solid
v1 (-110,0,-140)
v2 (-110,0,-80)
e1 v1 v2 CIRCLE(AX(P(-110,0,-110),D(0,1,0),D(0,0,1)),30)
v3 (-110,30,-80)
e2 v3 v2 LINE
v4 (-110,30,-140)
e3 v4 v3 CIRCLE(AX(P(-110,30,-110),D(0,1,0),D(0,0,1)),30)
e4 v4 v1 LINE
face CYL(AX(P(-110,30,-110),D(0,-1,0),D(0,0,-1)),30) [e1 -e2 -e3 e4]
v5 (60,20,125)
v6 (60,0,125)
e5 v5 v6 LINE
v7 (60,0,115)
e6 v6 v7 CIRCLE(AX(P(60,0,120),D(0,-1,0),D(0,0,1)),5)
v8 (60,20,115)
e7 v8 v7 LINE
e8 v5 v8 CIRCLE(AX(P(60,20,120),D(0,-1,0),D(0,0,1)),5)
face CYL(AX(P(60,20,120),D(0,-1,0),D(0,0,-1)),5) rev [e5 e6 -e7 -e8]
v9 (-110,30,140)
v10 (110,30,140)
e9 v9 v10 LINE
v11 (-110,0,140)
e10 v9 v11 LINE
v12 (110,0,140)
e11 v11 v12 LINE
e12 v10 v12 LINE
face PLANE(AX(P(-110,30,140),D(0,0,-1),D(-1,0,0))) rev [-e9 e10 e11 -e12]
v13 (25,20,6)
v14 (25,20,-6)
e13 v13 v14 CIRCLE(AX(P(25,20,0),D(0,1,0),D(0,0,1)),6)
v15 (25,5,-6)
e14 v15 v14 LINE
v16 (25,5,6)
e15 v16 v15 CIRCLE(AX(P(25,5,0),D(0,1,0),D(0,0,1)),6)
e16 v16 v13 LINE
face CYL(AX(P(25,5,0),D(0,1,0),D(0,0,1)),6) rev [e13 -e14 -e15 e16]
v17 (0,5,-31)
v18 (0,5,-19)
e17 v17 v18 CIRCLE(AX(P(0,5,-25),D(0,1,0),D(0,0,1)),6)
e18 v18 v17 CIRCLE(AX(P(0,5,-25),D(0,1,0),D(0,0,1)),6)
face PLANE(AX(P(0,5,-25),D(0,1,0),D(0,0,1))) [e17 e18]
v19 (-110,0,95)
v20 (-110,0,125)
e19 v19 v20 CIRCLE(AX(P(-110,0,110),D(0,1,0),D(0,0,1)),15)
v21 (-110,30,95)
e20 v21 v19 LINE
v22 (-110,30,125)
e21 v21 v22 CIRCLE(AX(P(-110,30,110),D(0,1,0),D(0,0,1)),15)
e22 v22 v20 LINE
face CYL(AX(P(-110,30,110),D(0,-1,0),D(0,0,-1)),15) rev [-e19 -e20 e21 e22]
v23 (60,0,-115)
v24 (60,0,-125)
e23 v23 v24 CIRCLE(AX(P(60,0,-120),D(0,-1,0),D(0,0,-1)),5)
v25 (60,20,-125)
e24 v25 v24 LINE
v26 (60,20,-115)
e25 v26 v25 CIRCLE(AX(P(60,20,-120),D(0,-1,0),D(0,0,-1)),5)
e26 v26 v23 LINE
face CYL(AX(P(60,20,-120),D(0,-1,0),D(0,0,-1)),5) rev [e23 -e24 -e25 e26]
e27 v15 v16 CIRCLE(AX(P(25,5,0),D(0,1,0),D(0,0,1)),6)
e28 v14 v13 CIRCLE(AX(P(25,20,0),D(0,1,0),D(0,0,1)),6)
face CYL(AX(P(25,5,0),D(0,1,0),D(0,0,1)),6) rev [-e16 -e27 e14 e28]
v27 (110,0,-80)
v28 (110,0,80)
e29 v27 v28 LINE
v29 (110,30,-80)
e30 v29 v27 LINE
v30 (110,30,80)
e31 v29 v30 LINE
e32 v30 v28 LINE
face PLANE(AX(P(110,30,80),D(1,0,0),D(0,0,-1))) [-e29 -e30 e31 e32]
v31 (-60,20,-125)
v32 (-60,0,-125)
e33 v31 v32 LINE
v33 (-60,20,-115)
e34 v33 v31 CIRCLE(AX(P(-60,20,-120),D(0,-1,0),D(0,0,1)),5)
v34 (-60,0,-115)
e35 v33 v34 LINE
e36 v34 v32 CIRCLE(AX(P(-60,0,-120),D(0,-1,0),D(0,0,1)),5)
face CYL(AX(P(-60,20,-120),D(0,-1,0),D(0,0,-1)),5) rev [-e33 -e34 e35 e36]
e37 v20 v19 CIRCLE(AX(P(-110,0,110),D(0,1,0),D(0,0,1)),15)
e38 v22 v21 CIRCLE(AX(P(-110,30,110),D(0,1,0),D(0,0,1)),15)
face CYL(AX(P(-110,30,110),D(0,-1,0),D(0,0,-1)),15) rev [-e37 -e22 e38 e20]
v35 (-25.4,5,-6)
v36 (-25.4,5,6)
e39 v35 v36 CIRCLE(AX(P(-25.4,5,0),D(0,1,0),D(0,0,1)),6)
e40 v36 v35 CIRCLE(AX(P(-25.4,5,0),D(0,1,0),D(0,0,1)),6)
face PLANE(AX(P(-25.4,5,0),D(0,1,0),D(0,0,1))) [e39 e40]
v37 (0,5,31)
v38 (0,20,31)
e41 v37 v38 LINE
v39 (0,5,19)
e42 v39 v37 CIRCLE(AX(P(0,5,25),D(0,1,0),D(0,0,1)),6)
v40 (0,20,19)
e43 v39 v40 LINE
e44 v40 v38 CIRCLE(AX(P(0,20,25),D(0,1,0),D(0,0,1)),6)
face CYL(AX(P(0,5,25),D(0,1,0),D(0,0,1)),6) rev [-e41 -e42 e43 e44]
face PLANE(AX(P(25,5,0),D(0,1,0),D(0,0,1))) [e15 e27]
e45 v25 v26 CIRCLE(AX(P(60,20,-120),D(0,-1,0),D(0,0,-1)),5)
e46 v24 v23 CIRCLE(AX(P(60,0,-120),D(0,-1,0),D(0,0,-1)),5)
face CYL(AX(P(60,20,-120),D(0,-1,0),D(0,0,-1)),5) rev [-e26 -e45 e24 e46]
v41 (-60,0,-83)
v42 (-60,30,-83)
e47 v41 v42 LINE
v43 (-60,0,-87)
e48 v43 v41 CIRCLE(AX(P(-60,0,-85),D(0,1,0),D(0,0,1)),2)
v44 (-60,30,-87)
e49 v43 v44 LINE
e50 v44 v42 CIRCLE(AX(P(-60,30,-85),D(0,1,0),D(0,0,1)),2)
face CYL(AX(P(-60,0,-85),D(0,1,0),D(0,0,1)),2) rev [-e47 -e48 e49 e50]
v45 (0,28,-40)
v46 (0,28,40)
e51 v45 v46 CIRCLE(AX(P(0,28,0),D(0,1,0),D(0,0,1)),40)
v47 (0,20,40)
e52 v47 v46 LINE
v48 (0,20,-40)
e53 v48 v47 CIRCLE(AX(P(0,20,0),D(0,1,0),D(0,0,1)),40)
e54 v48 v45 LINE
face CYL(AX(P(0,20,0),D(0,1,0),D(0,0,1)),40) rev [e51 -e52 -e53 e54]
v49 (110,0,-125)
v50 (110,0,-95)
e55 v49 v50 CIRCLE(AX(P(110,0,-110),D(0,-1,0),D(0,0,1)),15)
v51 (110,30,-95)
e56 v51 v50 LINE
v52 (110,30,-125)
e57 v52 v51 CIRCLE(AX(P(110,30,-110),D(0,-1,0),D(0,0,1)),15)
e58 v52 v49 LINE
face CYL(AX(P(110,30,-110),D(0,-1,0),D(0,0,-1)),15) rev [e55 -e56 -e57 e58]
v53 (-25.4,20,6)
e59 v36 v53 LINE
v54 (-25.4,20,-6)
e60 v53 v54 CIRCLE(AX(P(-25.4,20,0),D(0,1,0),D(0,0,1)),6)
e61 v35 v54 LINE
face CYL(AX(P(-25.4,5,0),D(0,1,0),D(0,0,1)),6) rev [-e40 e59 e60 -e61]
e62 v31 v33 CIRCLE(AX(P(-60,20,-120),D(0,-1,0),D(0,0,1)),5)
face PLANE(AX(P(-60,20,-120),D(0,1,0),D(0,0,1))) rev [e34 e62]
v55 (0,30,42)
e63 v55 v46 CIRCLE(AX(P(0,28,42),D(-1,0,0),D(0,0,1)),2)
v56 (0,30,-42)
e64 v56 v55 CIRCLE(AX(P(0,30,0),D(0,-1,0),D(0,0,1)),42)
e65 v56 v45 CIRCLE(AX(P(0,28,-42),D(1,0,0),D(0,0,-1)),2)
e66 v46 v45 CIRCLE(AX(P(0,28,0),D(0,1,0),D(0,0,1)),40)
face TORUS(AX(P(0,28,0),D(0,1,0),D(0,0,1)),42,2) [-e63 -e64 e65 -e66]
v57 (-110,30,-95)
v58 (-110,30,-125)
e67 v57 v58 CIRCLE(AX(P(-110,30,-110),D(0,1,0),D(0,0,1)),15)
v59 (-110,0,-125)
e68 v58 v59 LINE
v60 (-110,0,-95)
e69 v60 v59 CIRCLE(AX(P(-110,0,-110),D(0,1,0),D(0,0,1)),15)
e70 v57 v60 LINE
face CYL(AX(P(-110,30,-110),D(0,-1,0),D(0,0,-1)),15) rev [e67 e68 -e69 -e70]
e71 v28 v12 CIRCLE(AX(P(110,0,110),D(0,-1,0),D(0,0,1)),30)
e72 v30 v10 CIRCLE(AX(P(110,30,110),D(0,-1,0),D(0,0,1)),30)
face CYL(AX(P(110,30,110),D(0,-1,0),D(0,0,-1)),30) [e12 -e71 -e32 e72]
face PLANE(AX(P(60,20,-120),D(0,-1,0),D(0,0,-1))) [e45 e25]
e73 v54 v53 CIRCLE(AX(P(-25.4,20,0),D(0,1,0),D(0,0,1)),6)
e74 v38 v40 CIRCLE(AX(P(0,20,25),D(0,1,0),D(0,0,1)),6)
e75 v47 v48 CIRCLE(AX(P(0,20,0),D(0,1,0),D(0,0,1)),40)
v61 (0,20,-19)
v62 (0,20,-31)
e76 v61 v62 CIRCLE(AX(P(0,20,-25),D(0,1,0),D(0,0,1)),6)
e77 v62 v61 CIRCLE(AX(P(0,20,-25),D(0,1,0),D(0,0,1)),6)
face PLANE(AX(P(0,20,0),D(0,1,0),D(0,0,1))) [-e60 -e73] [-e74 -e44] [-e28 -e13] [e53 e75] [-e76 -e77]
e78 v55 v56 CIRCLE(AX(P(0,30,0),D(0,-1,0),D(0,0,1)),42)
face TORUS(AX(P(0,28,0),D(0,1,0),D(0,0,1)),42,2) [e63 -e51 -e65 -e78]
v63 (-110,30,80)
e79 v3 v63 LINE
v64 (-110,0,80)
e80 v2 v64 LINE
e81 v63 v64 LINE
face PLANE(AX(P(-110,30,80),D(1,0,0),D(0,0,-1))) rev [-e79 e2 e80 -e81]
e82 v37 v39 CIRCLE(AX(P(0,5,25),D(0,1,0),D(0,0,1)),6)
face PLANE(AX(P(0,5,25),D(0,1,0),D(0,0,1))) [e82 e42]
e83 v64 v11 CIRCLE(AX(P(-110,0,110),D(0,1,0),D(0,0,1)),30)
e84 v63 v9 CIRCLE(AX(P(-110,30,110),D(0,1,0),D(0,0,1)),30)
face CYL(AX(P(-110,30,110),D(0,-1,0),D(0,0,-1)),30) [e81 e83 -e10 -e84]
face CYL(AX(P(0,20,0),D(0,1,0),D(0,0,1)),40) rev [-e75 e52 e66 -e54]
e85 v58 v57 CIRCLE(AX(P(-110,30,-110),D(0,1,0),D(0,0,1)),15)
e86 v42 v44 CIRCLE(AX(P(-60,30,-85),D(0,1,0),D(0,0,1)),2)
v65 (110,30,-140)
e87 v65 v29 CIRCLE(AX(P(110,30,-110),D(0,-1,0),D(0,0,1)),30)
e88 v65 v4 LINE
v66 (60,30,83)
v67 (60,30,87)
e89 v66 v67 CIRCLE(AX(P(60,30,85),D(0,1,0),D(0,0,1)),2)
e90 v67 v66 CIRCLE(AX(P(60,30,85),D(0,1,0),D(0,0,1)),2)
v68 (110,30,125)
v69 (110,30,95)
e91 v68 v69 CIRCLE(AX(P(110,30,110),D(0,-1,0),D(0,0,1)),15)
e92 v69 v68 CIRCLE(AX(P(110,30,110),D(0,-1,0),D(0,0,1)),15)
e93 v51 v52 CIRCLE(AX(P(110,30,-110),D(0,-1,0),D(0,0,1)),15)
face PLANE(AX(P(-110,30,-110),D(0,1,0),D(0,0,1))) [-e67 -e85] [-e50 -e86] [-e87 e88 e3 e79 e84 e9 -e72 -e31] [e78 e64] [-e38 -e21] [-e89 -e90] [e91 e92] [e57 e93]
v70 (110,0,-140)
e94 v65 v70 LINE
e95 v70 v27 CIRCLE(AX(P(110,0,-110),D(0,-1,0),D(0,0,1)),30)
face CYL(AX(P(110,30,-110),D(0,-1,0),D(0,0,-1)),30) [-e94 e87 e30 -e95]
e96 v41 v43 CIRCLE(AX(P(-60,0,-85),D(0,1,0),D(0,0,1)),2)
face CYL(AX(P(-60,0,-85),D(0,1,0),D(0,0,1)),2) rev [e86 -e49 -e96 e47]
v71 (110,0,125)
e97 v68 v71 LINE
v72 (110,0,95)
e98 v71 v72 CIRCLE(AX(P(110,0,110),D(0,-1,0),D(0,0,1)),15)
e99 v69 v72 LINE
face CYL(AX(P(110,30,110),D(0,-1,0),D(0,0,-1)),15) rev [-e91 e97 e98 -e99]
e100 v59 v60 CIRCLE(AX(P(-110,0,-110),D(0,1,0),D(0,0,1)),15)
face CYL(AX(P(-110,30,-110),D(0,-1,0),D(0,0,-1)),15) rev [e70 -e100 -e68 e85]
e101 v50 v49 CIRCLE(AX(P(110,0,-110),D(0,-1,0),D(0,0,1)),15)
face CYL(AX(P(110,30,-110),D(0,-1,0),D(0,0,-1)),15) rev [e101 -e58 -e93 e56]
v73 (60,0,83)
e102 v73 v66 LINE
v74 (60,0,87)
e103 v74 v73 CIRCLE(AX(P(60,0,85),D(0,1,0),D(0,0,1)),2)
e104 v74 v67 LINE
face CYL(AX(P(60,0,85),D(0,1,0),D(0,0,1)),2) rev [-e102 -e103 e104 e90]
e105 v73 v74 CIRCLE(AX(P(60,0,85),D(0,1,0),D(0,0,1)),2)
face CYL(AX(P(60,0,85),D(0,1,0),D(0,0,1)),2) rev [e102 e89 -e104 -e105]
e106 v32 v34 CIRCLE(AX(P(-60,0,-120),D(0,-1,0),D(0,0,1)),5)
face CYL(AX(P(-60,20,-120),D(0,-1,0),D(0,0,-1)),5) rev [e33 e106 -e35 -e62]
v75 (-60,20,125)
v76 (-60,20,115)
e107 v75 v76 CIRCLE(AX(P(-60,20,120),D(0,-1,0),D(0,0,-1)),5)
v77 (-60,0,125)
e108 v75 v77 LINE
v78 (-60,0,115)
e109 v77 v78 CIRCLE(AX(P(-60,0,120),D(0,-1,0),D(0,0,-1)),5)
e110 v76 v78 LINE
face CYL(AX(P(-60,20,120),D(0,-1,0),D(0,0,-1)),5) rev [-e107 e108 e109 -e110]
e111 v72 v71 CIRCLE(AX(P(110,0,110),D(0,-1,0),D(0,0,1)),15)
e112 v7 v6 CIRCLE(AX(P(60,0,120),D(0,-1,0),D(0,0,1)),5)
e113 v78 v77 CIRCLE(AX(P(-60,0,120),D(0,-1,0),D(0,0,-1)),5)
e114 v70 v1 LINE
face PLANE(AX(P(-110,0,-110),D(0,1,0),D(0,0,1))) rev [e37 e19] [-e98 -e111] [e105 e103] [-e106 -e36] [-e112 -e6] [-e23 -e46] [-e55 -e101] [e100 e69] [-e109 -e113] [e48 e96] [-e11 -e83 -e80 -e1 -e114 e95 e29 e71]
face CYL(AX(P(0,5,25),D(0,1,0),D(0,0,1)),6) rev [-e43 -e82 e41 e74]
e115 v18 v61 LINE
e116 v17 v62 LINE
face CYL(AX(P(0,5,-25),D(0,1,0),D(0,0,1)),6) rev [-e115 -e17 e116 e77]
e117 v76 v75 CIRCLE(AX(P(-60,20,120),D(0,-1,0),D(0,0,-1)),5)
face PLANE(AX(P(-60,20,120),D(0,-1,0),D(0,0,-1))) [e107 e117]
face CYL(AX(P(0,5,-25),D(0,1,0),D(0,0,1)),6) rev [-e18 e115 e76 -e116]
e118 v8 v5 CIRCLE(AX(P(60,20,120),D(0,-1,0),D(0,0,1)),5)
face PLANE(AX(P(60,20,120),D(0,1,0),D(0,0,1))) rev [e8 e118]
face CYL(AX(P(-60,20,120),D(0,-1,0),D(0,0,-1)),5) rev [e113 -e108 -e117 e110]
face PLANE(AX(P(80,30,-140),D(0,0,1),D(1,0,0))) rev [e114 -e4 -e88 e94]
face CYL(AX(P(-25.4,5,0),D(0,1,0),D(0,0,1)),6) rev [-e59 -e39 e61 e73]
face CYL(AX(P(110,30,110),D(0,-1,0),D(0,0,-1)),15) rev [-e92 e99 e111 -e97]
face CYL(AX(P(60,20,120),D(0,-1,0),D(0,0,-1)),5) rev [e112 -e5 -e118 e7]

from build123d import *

# Parameters (mm, degrees)
SKETCH1_R                                        = 15
BOSS_EXTRUDE1_DEPTH                              = 30
CBORE_FOR_M8_PAN_HEAD_MACHINE_SCREW1_D           = 9
CBORE_FOR_M8_PAN_HEAD_MACHINE_SCREW1_CBORE_D     = 18
CBORE_FOR_M8_PAN_HEAD_MACHINE_SCREW1_CBORE_DEPTH = 6
SKETCH_1_R                                       = 2
CUT_EXTRUDE1_DEPTH                               = 201.249843945
SKETCH_3_R                                       = 5
CUT_EXTRUDE3_DEPTH                               = 20
SKETCH_4_R                                       = 40
CUT_EXTRUDE4_DEPTH                               = 10
FILLET1_R                                        = 2
SKETCH5_R                                        = 6
CUT_EXTRUDE7_DEPTH                               = 15


with BuildPart() as part:
    # Sketch1 → Boss-Extrude1 (new body)
    with BuildSketch(Plane(origin=(0, 0, 0), x_dir=(1, 0, 0), z_dir=(0, 1, 0))):
        with BuildLine():
            Line((-110, -140), (80, -140))
            Line((80, -140), (80, 140))
            Line((80, 140), (-110, 140))
            ThreePointArc((-110, 140), (-140, 110), (-110, 80))
            Line((-110, 80), (-110, -80))
            ThreePointArc((-110, -80), (-140, -110), (-110, -140))
        make_face()
        with Locations(Location((-110, 110, 0), (0, 0, 270))):
            Circle(SKETCH1_R, mode=Mode.SUBTRACT)
        with Locations(Location((-110, -110, 0), (0, 0, 270))):
            Circle(SKETCH1_R, mode=Mode.SUBTRACT)
    boss_extrude1 = extrude(amount=BOSS_EXTRUDE1_DEPTH)

    # CBORE for M8 Pan Head Machine Screw1 (through all)
    with Locations(Plane(origin=(0, 30, 0), x_dir=(1, 0, 0), z_dir=(0, 1, 0))):
        with Locations((60, 120), (-60, 120), (-60, -120), (60, -120)):
            CounterBoreHole(CBORE_FOR_M8_PAN_HEAD_MACHINE_SCREW1_D / 2, CBORE_FOR_M8_PAN_HEAD_MACHINE_SCREW1_CBORE_D / 2, CBORE_FOR_M8_PAN_HEAD_MACHINE_SCREW1_CBORE_DEPTH)

    # Mirror1: Boss-Extrude1 across plane
    add(boss_extrude1.mirror(Plane(origin=(0, 0, 0), x_dir=(0, 0, 1), z_dir=(1, 0, 0))))

    # 草图1 → Cut-Extrude1 (cut, through all)
    with BuildSketch(Plane(origin=(0, 30, 0), x_dir=(1, 0, 0), z_dir=(0, 1, 0))):
        with Locations(Location((-60, 85, 0), (0, 0, 270))):
            Circle(SKETCH_1_R)
        with Locations(Location((60, -85, 0), (0, 0, 270))):
            Circle(SKETCH_1_R)
    extrude(amount=-CUT_EXTRUDE1_DEPTH, mode=Mode.SUBTRACT)

    # 草图3 → Cut-Extrude3 (cut)
    with BuildSketch(Plane.XZ):
        with Locations(Location((-60, 120, 0), (0, 0, 270))):
            Circle(SKETCH_3_R)
        with Locations(Location((60, 120, 0), (0, 0, 90))):
            Circle(SKETCH_3_R)
        with Locations(Location((60, -120, 0), (0, 0, 270))):
            Circle(SKETCH_3_R)
        with Locations(Location((-60, -120, 0), (0, 0, 90))):
            Circle(SKETCH_3_R)
    extrude(amount=-CUT_EXTRUDE3_DEPTH, mode=Mode.SUBTRACT)

    # 草图4 → Cut-Extrude4 (cut)
    with BuildSketch(Plane(origin=(0, 30, 0), x_dir=(1, 0, 0), z_dir=(0, 1, 0))):
        with Locations(Location((0, 0, 0), (0, 0, 270))):
            Circle(SKETCH_4_R)
    extrude(amount=-CUT_EXTRUDE4_DEPTH, mode=Mode.SUBTRACT)

    # Fillet1
    fillet1_edges = [part.edges().sort_by_distance(p)[0] for p in [
        (0, 30, -40),
    ]]
    fillet(fillet1_edges, radius=FILLET1_R)

    # Sketch5 → Cut-Extrude7 (cut)
    with BuildSketch(Plane(origin=(0, 20, 0), x_dir=(1, 0, 0), z_dir=(0, 1, 0))):
        with Locations(Location((0, 25, 0), (0, 0, 270))):
            Circle(SKETCH5_R)
        with Locations(Location((-25.4, 0, 0), (0, 0, 270))):
            Circle(SKETCH5_R)
        with Locations(Location((25, 0, 0), (0, 0, 270))):
            Circle(SKETCH5_R)
        with Locations(Location((0, -25, 0), (0, 0, 270))):
            Circle(SKETCH5_R)
    extrude(amount=-CUT_EXTRUDE7_DEPTH, mode=Mode.SUBTRACT)


solid = part.part
